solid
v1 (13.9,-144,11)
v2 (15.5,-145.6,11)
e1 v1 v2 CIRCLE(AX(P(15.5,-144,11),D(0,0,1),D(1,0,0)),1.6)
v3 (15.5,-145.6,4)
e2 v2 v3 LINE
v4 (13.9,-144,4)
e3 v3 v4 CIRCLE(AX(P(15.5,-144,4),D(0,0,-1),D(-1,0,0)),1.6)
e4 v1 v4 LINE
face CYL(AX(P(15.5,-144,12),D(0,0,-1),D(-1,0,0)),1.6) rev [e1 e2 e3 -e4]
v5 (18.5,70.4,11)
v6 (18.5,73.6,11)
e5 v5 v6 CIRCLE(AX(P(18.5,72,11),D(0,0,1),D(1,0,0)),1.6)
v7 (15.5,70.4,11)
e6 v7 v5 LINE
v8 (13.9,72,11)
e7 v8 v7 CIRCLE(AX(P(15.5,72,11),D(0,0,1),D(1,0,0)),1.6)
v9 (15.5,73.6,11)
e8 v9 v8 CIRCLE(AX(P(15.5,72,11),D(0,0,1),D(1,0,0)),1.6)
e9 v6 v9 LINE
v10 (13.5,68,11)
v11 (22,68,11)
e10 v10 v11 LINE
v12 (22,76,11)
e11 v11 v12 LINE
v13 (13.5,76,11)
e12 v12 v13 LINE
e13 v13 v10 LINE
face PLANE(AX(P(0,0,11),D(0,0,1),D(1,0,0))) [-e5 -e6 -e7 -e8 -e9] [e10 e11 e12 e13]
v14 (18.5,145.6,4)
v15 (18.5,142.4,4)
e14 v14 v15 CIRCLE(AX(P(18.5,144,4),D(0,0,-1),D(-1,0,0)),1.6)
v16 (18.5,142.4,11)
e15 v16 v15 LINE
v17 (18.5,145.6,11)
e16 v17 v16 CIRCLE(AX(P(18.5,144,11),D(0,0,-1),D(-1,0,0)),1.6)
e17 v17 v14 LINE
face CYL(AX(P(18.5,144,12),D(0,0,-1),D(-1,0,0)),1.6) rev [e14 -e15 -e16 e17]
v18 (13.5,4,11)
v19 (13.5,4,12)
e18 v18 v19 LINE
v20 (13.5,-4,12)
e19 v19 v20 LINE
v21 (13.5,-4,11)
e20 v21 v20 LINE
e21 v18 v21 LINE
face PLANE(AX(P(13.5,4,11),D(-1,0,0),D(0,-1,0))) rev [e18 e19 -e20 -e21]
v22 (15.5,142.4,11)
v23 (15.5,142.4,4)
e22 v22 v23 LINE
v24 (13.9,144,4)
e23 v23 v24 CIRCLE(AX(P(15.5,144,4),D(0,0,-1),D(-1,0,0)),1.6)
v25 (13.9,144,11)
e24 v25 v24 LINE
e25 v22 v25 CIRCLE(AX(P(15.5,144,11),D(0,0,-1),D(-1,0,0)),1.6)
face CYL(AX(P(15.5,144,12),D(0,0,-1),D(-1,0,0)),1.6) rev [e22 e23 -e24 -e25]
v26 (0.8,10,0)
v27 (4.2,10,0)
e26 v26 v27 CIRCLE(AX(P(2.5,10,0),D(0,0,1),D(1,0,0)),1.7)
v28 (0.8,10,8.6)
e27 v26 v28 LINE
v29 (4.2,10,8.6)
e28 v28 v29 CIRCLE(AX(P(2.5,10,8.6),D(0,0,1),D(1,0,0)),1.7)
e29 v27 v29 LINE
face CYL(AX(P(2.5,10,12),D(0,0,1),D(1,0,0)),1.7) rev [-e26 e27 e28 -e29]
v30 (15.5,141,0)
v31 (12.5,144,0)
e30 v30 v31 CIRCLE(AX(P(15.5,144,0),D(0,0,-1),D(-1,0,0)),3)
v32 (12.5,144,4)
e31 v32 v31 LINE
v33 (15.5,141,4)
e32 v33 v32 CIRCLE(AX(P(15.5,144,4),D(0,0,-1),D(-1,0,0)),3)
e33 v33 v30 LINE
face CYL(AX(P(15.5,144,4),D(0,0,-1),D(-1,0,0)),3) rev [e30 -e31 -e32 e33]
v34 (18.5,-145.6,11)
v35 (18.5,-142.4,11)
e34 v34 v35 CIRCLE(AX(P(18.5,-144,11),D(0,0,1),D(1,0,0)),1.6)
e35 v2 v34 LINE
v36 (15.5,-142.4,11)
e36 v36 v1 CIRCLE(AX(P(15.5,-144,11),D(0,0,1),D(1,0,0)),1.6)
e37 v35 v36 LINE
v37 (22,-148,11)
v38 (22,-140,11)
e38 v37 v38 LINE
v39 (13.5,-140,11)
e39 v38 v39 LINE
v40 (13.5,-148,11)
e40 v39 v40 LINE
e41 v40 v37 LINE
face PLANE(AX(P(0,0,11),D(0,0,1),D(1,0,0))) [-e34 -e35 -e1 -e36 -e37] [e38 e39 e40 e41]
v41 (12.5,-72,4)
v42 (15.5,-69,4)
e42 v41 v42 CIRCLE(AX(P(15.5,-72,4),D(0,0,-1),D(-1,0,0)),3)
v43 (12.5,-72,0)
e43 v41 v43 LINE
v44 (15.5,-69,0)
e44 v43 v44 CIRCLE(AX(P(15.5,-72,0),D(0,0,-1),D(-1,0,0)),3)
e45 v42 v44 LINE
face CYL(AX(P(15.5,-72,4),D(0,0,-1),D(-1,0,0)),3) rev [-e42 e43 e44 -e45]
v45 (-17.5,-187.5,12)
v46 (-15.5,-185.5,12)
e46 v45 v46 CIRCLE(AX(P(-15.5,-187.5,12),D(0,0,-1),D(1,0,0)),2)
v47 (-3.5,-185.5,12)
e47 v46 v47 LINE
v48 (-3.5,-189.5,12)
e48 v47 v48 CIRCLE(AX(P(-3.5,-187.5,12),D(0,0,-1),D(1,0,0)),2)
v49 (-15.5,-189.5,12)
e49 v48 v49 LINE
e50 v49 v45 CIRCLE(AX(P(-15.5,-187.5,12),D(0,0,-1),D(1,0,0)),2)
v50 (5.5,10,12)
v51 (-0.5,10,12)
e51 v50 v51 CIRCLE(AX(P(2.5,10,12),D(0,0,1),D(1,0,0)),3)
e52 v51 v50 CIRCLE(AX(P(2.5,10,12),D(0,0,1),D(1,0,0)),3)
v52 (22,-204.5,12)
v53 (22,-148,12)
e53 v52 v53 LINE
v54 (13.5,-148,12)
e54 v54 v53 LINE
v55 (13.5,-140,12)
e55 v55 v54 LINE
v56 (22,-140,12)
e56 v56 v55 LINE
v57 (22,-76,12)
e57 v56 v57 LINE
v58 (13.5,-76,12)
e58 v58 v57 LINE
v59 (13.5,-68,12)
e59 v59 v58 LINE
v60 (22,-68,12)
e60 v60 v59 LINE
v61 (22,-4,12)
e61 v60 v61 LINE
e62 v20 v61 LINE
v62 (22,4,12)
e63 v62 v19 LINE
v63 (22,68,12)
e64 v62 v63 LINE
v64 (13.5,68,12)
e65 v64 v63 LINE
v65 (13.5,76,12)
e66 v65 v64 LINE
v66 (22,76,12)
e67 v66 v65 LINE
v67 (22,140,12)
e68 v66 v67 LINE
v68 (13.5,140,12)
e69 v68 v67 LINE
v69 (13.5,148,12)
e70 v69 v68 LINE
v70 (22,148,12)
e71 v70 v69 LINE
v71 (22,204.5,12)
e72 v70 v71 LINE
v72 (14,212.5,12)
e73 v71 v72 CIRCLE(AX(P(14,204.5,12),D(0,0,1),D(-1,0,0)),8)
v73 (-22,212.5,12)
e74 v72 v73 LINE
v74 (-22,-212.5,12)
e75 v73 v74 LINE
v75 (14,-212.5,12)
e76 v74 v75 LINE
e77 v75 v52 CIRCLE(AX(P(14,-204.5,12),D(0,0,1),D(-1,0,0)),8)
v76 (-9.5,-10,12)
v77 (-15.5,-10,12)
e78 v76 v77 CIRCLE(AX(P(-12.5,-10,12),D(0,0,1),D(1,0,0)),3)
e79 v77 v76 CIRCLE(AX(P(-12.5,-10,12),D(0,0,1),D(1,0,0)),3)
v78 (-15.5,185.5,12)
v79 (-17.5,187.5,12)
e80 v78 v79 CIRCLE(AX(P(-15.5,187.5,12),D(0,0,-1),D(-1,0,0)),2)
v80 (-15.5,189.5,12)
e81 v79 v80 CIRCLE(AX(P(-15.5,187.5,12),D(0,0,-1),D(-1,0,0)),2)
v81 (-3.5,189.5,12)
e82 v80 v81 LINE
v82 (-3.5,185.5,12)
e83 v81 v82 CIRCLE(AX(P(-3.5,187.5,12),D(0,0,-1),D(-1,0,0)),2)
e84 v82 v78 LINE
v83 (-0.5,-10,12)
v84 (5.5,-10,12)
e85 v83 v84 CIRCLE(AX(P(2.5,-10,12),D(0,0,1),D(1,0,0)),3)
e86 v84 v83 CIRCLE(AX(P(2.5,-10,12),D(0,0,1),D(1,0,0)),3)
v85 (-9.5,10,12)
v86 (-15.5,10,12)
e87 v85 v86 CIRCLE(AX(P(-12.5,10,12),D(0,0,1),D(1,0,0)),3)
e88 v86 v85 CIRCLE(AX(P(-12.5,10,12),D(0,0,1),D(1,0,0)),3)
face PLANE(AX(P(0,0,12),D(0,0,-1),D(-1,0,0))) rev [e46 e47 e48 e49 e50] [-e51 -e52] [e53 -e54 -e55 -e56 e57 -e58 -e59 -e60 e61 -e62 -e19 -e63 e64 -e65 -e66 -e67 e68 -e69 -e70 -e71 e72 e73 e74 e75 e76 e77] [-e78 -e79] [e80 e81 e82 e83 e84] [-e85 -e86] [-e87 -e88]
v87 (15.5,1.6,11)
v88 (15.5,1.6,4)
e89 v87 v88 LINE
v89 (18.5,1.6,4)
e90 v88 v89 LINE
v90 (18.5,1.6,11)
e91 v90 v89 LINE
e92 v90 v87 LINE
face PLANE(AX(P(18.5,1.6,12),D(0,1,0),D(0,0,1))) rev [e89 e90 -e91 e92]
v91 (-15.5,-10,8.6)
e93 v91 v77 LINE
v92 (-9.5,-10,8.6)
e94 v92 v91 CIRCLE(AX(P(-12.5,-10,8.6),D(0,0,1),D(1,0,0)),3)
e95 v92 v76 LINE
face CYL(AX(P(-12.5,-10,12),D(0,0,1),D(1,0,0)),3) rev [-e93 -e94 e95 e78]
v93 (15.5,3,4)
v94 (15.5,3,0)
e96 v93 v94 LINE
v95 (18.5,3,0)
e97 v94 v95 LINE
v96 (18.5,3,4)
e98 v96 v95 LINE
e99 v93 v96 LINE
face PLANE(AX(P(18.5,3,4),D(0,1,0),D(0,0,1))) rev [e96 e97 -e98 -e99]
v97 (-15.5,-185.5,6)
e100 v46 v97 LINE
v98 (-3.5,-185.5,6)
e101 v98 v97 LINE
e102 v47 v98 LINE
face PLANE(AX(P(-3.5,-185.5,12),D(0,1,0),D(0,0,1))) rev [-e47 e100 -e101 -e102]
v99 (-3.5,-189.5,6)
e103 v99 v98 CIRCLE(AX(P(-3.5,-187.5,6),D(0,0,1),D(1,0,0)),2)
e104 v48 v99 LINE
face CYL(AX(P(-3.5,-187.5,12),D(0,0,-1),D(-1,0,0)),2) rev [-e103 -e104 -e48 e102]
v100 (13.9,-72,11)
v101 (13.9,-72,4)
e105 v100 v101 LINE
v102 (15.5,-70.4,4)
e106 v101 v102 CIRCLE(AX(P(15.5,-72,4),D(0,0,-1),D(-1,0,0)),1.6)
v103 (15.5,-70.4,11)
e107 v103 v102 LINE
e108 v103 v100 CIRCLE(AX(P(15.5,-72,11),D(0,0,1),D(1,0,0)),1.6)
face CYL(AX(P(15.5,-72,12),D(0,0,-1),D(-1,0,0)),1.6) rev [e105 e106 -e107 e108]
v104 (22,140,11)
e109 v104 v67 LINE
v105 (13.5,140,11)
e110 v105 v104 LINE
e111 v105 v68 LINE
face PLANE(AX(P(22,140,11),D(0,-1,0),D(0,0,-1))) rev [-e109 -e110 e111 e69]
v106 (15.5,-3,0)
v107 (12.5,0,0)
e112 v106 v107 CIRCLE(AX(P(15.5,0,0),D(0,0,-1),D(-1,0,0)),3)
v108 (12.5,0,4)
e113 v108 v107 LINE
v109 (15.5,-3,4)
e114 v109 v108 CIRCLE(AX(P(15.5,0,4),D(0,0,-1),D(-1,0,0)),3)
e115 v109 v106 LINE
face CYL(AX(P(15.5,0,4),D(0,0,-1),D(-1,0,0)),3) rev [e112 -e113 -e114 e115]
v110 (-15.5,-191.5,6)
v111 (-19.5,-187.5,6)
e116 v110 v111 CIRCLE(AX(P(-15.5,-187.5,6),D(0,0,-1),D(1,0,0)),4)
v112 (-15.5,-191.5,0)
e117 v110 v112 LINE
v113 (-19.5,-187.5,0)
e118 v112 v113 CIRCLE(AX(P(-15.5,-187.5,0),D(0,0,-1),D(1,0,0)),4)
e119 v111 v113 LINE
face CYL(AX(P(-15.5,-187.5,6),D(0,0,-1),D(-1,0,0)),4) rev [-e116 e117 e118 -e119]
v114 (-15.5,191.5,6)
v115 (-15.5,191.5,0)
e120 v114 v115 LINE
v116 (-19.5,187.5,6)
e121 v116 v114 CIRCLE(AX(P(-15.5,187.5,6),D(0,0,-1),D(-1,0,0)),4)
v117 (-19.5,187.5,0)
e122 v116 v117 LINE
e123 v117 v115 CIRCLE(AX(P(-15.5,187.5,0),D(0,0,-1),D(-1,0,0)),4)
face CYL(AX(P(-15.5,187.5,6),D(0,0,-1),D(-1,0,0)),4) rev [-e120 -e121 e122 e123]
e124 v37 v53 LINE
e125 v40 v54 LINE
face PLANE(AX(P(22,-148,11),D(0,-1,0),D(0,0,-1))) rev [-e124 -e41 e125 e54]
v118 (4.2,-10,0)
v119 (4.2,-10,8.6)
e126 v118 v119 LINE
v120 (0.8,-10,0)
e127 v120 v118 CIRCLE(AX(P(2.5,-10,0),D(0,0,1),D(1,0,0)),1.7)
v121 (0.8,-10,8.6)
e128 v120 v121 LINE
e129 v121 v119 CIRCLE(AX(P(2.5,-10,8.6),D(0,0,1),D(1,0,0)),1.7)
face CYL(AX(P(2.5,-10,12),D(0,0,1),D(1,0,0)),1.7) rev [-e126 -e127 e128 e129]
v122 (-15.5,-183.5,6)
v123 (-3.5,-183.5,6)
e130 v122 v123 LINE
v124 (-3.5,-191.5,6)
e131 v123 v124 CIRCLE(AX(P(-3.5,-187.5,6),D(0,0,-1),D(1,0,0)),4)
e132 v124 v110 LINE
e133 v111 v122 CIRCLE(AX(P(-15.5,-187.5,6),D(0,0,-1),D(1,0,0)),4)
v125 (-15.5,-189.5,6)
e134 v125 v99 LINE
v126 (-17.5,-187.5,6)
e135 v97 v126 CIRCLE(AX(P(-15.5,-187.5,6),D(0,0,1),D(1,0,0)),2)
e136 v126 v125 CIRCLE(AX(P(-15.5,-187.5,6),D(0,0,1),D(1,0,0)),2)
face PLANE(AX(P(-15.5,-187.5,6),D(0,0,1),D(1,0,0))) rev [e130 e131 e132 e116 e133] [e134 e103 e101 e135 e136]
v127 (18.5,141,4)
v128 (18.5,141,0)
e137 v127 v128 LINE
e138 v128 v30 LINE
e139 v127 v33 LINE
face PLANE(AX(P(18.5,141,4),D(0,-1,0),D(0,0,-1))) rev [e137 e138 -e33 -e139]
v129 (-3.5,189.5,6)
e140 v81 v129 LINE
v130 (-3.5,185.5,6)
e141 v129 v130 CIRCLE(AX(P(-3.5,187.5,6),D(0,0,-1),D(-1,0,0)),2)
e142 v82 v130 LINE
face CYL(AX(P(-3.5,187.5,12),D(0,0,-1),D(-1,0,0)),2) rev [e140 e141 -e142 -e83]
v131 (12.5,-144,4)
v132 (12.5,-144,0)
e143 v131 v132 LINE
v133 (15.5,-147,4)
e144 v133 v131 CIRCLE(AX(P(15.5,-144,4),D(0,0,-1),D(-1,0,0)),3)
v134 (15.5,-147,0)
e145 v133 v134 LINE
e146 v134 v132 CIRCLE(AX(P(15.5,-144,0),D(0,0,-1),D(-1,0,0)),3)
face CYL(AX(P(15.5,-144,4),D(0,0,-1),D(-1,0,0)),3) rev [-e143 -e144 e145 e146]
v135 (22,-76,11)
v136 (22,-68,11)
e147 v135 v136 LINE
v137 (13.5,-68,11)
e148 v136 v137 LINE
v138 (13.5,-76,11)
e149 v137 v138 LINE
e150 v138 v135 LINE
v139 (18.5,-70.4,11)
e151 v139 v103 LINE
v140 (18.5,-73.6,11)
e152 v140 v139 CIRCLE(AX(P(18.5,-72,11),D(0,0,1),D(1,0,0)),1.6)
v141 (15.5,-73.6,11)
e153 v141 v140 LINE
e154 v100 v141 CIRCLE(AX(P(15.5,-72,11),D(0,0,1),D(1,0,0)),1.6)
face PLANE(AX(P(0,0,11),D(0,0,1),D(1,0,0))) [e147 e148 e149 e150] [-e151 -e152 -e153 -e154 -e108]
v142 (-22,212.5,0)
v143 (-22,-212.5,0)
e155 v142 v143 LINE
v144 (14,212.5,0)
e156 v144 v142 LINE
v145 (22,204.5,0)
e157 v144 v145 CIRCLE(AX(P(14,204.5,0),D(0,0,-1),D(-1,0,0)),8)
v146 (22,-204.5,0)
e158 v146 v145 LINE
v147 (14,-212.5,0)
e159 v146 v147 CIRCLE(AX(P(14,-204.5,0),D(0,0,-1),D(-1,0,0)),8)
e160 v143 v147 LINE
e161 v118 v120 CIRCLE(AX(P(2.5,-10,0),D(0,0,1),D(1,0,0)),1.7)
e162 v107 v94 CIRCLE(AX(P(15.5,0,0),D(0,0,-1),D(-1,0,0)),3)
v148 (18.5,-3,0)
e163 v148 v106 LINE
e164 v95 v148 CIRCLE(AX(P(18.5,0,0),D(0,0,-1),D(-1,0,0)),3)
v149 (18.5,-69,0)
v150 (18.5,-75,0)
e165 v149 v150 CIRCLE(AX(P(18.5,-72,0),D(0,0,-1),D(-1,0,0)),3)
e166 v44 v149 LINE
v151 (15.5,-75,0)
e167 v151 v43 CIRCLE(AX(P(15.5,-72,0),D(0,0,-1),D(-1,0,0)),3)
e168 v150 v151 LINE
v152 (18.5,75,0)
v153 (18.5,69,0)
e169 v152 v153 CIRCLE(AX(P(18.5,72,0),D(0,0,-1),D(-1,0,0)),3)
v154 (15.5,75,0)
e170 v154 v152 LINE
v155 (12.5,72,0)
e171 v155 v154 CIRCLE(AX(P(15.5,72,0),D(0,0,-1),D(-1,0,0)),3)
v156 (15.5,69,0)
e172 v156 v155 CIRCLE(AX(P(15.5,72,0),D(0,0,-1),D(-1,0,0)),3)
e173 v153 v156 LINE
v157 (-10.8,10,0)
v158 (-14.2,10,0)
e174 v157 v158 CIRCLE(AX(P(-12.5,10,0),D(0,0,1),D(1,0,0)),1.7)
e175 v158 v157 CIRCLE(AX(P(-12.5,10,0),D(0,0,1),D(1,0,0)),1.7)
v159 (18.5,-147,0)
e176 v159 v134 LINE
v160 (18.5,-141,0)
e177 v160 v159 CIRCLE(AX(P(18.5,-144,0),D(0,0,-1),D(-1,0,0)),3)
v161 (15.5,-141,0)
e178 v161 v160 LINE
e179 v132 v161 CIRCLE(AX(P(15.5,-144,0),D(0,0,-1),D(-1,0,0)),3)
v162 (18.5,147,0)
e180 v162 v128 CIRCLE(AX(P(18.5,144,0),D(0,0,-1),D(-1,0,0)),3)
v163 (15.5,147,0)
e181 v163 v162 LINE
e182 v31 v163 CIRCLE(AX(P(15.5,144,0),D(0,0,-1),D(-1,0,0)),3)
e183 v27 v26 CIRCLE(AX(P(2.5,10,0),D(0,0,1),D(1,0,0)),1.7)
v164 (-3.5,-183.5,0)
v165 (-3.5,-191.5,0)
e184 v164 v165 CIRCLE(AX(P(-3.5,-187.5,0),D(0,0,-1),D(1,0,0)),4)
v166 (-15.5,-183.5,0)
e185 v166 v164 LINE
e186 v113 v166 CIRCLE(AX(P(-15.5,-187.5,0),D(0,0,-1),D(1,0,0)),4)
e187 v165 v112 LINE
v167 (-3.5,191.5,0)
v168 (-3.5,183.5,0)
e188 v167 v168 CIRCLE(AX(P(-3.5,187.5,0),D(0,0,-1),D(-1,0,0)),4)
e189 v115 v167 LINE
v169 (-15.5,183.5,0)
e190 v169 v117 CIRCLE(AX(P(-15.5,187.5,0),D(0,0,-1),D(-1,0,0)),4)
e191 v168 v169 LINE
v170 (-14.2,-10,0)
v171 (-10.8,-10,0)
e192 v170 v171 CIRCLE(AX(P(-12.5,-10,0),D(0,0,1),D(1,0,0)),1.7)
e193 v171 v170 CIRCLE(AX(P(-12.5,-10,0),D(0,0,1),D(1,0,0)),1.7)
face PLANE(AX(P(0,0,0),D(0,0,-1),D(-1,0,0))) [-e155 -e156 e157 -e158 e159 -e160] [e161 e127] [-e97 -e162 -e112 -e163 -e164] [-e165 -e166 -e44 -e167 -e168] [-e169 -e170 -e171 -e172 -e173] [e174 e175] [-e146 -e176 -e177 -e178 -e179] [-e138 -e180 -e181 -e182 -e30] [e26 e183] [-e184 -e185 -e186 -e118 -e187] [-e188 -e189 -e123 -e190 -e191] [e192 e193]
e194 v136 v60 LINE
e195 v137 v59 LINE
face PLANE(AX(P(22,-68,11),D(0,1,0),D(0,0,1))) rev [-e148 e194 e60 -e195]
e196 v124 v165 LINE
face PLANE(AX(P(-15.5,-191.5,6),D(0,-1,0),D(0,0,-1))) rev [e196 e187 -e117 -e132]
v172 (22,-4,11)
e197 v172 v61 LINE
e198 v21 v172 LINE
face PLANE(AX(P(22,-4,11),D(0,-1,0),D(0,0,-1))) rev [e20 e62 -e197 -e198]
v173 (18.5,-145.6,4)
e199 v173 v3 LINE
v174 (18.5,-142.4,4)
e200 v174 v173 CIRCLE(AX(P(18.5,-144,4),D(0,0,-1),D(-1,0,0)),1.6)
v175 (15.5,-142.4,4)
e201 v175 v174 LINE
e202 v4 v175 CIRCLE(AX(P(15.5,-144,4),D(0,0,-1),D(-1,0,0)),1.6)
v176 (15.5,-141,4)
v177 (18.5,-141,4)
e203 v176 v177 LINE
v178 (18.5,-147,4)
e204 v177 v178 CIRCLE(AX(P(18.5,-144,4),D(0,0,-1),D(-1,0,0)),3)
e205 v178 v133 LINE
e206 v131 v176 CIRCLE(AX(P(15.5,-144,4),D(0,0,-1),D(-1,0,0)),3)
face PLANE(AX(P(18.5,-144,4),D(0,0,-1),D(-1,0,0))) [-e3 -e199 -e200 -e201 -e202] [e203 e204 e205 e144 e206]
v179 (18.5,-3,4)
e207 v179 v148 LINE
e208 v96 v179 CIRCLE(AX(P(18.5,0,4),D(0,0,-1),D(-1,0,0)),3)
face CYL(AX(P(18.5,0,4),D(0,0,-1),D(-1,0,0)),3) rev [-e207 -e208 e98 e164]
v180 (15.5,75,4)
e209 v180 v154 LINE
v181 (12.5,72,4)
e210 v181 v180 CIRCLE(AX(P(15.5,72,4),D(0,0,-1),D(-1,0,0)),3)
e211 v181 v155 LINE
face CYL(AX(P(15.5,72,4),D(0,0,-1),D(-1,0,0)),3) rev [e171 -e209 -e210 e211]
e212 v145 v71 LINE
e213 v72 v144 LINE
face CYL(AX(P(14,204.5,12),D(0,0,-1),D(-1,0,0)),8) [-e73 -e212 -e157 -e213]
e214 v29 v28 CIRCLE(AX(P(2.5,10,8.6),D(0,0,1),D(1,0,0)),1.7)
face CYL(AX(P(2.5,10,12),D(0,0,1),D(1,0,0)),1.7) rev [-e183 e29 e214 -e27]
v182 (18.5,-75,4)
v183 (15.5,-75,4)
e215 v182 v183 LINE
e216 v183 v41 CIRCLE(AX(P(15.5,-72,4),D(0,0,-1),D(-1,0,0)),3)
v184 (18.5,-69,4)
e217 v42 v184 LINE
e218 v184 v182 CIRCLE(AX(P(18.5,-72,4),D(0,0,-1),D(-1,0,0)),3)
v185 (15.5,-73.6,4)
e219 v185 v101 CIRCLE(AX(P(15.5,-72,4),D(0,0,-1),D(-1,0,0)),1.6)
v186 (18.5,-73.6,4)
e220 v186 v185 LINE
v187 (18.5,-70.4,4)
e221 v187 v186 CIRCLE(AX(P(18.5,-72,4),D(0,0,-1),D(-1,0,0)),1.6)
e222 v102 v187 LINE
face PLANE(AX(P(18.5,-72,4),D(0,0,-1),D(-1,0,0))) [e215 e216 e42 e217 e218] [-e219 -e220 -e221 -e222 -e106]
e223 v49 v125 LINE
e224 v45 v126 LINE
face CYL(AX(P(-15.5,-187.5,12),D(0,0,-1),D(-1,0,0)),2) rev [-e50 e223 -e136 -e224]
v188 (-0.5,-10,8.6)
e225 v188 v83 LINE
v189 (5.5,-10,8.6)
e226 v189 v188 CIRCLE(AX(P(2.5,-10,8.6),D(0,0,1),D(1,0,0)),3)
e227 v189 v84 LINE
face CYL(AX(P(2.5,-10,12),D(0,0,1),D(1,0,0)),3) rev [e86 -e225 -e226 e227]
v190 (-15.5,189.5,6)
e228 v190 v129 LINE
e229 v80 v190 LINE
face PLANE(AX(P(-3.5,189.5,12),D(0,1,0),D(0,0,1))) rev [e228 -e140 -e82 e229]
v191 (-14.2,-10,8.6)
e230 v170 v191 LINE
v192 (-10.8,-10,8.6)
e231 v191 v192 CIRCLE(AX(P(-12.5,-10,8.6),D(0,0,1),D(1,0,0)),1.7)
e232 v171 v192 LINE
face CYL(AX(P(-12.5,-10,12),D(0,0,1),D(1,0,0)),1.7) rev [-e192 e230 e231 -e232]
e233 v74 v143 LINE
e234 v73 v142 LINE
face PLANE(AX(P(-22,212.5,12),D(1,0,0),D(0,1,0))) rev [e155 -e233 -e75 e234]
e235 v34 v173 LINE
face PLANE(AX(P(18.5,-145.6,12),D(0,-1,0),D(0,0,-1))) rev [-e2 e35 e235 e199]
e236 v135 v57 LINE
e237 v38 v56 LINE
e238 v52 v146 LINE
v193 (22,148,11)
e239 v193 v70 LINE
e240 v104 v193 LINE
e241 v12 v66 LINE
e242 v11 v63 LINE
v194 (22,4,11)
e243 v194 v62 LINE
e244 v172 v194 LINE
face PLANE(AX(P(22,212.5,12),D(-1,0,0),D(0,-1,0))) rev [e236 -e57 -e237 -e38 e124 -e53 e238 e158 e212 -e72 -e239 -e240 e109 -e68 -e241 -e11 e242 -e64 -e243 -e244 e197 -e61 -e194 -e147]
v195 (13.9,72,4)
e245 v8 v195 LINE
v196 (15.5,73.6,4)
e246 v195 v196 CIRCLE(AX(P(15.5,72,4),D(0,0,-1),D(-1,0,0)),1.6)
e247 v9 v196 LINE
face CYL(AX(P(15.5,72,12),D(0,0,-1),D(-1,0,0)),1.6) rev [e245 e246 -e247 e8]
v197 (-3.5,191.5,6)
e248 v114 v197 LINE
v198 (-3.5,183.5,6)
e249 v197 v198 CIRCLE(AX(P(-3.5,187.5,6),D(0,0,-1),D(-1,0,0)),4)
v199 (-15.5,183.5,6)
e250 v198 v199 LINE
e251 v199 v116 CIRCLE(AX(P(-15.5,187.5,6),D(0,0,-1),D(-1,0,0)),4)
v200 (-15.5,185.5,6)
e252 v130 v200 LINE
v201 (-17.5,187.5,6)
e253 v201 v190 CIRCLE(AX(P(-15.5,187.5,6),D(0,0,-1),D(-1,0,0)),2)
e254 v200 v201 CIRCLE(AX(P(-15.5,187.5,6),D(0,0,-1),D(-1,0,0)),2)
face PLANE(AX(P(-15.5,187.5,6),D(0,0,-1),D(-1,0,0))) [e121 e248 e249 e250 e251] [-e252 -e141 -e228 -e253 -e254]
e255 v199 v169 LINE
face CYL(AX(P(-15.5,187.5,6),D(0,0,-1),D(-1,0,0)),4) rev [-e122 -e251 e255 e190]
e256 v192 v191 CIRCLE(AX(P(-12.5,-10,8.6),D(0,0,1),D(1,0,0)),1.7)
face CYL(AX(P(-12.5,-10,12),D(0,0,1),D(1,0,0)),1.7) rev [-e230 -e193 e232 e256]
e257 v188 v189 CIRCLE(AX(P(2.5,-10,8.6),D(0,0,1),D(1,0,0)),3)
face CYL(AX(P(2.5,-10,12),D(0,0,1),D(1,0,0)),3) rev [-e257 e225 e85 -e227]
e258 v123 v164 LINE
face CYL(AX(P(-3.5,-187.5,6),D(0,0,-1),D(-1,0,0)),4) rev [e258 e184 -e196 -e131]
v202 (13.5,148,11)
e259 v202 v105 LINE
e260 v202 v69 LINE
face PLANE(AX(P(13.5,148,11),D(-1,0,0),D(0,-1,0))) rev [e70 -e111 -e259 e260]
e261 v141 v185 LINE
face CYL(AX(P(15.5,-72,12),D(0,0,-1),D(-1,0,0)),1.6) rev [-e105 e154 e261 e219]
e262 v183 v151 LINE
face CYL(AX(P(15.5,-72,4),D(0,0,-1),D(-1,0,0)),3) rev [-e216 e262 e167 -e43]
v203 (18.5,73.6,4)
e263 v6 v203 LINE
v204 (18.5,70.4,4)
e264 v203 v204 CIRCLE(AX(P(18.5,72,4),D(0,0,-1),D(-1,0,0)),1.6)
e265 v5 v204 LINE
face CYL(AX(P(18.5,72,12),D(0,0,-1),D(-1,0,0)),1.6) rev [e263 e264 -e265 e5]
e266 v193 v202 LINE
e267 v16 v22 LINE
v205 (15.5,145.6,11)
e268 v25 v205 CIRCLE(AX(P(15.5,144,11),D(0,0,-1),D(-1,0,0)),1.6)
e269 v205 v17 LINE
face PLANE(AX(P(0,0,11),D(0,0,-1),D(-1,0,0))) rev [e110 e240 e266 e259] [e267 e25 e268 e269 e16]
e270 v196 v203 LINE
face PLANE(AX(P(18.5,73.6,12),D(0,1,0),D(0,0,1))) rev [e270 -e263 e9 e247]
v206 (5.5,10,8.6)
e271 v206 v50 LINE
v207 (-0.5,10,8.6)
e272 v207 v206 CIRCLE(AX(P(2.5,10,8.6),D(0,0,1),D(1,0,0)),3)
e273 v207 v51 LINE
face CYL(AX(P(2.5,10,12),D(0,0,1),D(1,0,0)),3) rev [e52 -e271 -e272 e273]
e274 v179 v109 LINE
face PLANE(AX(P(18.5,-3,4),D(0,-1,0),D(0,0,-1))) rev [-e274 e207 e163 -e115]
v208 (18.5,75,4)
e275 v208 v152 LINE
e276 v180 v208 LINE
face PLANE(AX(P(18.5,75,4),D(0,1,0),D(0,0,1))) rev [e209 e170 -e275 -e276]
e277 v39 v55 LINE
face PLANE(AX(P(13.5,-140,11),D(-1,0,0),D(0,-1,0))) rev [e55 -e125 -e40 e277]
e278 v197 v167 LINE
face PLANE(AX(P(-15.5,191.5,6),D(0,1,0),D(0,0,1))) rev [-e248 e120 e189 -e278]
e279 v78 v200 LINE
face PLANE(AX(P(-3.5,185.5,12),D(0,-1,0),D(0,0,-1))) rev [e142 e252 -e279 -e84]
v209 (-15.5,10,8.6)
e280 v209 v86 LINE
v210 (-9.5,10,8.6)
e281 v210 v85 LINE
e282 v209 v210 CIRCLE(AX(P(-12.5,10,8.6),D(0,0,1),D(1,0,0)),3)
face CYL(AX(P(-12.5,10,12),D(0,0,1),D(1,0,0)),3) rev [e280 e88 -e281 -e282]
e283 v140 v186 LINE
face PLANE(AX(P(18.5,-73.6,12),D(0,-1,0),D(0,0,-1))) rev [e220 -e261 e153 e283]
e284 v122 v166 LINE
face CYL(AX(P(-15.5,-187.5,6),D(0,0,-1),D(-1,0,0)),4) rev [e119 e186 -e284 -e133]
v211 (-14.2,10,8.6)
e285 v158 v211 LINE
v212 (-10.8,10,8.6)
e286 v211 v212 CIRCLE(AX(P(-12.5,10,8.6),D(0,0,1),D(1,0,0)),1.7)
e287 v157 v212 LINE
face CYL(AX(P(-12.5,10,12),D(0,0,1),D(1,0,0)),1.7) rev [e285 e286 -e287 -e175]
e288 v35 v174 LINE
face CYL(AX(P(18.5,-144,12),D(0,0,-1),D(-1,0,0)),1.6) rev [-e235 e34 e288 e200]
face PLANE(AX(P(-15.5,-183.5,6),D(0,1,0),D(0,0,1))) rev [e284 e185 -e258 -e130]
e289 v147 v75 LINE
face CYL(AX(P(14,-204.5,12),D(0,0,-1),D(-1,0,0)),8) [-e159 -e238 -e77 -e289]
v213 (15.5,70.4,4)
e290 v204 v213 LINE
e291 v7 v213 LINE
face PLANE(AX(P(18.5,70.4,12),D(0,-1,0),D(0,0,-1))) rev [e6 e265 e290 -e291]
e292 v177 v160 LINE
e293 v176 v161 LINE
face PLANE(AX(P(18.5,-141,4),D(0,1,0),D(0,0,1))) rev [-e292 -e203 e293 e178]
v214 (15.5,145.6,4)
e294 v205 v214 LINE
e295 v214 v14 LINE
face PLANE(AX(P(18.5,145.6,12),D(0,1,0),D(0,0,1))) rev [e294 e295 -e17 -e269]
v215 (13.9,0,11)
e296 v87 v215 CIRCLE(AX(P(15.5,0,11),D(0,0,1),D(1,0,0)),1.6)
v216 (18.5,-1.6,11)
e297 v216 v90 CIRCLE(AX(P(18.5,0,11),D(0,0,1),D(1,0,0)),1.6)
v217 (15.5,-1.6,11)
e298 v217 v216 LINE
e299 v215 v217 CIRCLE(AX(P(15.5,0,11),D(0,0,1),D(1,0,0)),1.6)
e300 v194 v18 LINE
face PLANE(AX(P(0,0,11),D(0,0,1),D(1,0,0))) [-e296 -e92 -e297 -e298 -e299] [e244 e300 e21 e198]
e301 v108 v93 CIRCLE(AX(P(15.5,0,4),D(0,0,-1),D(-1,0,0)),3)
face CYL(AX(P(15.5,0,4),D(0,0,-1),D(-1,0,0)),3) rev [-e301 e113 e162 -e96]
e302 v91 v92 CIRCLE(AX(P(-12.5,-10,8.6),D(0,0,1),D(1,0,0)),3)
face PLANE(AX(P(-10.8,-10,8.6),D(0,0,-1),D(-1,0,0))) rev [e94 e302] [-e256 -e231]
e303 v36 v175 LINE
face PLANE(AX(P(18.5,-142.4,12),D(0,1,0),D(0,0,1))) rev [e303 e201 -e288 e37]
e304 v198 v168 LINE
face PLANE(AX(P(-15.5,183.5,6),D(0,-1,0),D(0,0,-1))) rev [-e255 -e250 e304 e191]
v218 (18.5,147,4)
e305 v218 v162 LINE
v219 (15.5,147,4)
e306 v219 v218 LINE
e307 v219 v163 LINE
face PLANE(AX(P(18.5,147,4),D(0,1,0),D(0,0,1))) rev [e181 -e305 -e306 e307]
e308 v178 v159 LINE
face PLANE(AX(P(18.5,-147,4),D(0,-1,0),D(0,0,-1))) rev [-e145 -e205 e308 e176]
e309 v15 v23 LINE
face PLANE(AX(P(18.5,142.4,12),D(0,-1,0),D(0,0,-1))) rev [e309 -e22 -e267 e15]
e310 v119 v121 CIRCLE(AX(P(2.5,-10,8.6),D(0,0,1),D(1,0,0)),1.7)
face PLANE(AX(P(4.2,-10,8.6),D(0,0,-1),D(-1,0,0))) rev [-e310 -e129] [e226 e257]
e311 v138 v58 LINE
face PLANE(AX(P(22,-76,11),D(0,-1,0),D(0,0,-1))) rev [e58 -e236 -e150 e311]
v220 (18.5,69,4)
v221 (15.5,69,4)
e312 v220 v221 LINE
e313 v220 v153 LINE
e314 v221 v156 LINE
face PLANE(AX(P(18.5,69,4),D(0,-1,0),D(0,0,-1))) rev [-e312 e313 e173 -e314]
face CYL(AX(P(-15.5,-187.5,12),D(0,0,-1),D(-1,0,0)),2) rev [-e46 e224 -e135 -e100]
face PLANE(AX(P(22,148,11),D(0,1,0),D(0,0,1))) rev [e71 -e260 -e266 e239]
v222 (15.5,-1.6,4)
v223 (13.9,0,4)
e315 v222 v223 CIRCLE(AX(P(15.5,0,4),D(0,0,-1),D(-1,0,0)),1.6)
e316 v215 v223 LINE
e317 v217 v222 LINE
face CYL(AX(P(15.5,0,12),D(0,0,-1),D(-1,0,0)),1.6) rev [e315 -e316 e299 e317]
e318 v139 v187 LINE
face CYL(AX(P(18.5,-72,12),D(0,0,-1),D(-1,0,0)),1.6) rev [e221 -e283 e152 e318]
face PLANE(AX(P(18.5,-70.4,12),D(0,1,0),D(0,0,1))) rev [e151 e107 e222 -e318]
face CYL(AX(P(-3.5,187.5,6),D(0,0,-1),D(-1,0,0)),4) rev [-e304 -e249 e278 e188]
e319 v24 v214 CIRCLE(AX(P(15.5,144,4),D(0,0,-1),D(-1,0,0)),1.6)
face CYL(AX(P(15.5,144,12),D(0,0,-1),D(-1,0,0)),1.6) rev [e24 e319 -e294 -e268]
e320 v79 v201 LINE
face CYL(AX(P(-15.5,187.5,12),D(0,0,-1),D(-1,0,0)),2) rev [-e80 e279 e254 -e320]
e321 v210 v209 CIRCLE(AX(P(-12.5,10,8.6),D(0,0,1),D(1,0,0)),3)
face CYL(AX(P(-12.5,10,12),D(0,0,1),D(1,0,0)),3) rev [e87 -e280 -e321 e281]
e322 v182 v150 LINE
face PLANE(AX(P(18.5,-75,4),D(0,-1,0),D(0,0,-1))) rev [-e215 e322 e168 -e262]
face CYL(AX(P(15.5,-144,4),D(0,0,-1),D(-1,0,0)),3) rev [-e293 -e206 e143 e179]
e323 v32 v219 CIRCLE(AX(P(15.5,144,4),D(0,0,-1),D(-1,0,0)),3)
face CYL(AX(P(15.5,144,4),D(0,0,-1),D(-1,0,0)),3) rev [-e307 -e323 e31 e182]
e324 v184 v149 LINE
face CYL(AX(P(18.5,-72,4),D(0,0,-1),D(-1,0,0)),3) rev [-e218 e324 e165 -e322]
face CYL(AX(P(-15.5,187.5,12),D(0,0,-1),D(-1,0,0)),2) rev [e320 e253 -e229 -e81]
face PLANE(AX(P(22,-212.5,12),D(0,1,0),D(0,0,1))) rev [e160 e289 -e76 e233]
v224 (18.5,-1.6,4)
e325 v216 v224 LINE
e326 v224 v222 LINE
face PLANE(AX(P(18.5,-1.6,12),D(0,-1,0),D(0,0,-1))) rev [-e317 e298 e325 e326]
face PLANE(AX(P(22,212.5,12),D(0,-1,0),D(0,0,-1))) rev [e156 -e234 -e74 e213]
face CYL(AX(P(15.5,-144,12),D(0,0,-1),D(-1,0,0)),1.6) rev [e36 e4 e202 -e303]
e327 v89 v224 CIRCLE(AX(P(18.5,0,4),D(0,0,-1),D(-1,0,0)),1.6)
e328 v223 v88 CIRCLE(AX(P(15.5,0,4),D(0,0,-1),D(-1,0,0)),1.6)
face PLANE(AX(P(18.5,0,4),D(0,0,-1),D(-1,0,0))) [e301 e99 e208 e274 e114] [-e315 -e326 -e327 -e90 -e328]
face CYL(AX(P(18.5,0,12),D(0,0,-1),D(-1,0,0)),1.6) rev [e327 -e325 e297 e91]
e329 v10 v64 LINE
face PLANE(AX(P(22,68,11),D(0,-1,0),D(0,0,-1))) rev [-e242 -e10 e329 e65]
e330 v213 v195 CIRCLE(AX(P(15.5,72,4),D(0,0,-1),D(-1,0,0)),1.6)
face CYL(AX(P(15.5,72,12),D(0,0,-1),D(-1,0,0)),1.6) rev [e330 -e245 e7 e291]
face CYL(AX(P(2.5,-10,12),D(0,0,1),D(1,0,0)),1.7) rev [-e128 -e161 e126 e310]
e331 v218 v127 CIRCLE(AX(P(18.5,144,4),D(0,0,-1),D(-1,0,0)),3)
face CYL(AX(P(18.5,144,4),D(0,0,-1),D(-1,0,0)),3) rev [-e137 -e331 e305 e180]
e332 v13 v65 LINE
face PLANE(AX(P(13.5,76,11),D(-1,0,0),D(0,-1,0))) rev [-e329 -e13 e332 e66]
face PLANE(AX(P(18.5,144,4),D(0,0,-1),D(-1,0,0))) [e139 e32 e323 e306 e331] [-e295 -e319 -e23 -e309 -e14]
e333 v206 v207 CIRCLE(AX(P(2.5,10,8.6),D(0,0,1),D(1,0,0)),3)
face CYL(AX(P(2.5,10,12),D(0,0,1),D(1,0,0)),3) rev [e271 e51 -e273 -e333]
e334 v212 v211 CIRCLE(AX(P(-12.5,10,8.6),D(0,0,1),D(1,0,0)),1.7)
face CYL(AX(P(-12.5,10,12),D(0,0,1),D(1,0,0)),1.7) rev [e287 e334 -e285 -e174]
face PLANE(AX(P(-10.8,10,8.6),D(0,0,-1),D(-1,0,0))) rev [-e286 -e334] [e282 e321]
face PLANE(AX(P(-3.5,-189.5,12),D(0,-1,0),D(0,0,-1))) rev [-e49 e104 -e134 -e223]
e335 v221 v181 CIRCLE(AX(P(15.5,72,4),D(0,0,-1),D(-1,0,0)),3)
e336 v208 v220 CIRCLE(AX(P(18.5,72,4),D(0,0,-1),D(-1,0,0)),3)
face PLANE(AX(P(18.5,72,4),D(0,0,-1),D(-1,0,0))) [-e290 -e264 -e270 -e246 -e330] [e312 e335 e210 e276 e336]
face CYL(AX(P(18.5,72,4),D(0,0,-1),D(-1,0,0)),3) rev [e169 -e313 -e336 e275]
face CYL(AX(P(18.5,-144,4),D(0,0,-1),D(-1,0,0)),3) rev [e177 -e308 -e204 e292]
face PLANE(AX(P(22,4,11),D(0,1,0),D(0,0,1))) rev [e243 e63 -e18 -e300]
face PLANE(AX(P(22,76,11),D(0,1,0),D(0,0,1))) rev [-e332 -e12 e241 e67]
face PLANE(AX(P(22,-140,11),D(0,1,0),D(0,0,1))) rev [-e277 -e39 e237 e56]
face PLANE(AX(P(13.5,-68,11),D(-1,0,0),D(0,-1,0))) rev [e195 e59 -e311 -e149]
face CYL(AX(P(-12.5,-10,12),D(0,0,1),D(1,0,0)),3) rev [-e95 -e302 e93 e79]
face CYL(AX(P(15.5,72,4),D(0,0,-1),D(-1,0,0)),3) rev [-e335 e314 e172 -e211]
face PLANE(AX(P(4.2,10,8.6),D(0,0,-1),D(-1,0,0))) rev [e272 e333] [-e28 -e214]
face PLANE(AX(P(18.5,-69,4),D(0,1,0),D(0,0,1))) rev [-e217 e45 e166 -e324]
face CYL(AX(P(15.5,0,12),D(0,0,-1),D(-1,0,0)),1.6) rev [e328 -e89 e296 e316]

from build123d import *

# Parameters (mm, degrees)
SKETCH_1_W                = 44
SKETCH_1_H                = 425
EXTRUDE_1_DEPTH           = 12
FILLET_1_R                = 8
CUT_EXTRUDE_1_DEPTH       = 6
CUT_EXTRUDE_2_DEPTH       = 214.972544968
SKETCH_5_W                = 8.5
SKETCH_5_H                = 8
CUT_EXTRUDE_3_DEPTH       = 1
CUT_EXTRUDE_4_DEPTH       = 4
CUT_EXTRUDE_5_DEPTH       = 214.785523364
PATTERN_LINEAR_1_COUNT    = 5
PATTERN_LINEAR_1_PITCH    = 72
HOLE_WIZARD_1_D           = 3.4
HOLE_WIZARD_1_CBORE_D     = 6
HOLE_WIZARD_1_CBORE_DEPTH = 3.4


with BuildPart() as part:
    # 草图1 → 凸台-拉伸1 (new body)
    with BuildSketch(Plane.XY):
        Rectangle(SKETCH_1_W, SKETCH_1_H)
    extrude(amount=EXTRUDE_1_DEPTH)

    # 圆角1
    fillet_1_edges = [part.edges().sort_by_distance(p)[0] for p in [
        (22, 212.5, 6),
        (22, -212.5, 6),
    ]]
    fillet(fillet_1_edges, radius=FILLET_1_R)

    # 草图3 → 切除-拉伸1 (cut)
    with BuildSketch(Plane(origin=(0, 0, 0), x_dir=(-1, 0, 0), z_dir=(0, 0, -1))):
        with BuildLine():
            Line((15.5, 183.5), (3.5, 183.5))
            ThreePointArc((3.5, 183.5), (-0.5, 187.5), (3.5, 191.5))
            Line((3.5, 191.5), (15.5, 191.5))
            ThreePointArc((15.5, 191.5), (19.5, 187.5), (15.5, 183.5))
        make_face()
        with BuildLine():
            Line((15.5, -183.5), (3.5, -183.5))
            ThreePointArc((3.5, -183.5), (-0.5, -187.5), (3.5, -191.5))
            Line((3.5, -191.5), (15.5, -191.5))
            ThreePointArc((15.5, -191.5), (19.5, -187.5), (15.5, -183.5))
        make_face()
    extrude(amount=-CUT_EXTRUDE_1_DEPTH, mode=Mode.SUBTRACT)

    # 草图4 → 切除-拉伸2 (cut, through all)
    with BuildSketch(Plane(origin=(0, 0, 0), x_dir=(-1, 0, 0), z_dir=(0, 0, -1))):
        with BuildLine():
            Line((3.5, 189.5), (15.5, 189.5))
            ThreePointArc((15.5, 189.5), (17.5, 187.5), (15.5, 185.5))
            Line((15.5, 185.5), (3.5, 185.5))
            ThreePointArc((3.5, 185.5), (1.5, 187.5), (3.5, 189.5))
        make_face()
        with BuildLine():
            Line((3.5, -189.5), (15.5, -189.5))
            ThreePointArc((15.5, -189.5), (17.5, -187.5), (15.5, -185.5))
            Line((15.5, -185.5), (3.5, -185.5))
            ThreePointArc((3.5, -185.5), (1.5, -187.5), (3.5, -189.5))
        make_face()
    extrude(amount=-CUT_EXTRUDE_2_DEPTH, mode=Mode.SUBTRACT)

    # 草图5 → 切除-拉伸3 (cut)
    with BuildSketch(Plane.XY.offset(12)):
        with Locations((17.75, 144)):
            Rectangle(SKETCH_5_W, SKETCH_5_H)
        with Locations((17.75, 72)):
            Rectangle(SKETCH_5_W, SKETCH_5_H)
        with Locations((17.75, 0)):
            Rectangle(SKETCH_5_W, SKETCH_5_H)
        with Locations((17.75, -72)):
            Rectangle(SKETCH_5_W, SKETCH_5_H)
        with Locations((17.75, -144)):
            Rectangle(SKETCH_5_W, SKETCH_5_H)
    extrude(amount=-CUT_EXTRUDE_3_DEPTH, mode=Mode.SUBTRACT)

    # 草图6 → 切除-拉伸4 (cut)
    with BuildSketch(Plane(origin=(0, 0, 0), x_dir=(-1, 0, 0), z_dir=(0, 0, -1))):
        with BuildLine():
            Line((-18.5, 147), (-15.5, 147))
            ThreePointArc((-15.5, 147), (-12.5, 144), (-15.5, 141))
            Line((-15.5, 141), (-18.5, 141))
            ThreePointArc((-18.5, 141), (-21.5, 144), (-18.5, 147))
        make_face()
    cut_extrude_4 = extrude(amount=-CUT_EXTRUDE_4_DEPTH, mode=Mode.SUBTRACT)

    # 草图7 → 切除-拉伸5 (cut, through all)
    with BuildSketch(Plane(origin=(0, 0, 4), x_dir=(-1, 0, 0), z_dir=(0, 0, -1))):
        with BuildLine():
            Line((-18.5, 145.6), (-15.5, 145.6))
            ThreePointArc((-15.5, 145.6), (-13.9, 144), (-15.5, 142.4))
            Line((-15.5, 142.4), (-18.5, 142.4))
            ThreePointArc((-18.5, 142.4), (-20.1, 144), (-18.5, 145.6))
        make_face()
    cut_extrude_5 = extrude(amount=-CUT_EXTRUDE_5_DEPTH, mode=Mode.SUBTRACT)

    # 阵列(线性)1: 切除-拉伸4, 切除-拉伸5 ×5
    with Locations(*[(0, -i * PATTERN_LINEAR_1_PITCH, 0) for i in range(1, PATTERN_LINEAR_1_COUNT)]):
        add(cut_extrude_4, mode=Mode.SUBTRACT)
        add(cut_extrude_5, mode=Mode.SUBTRACT)

    # 打孔尺寸根据内六角圆柱头螺钉的类型1 (through all)
    with Locations(Plane.XY.offset(12)):
        with Locations((2.5, 10), (-12.5, 10), (2.5, -10), (-12.5, -10)):
            CounterBoreHole(HOLE_WIZARD_1_D / 2, HOLE_WIZARD_1_CBORE_D / 2, HOLE_WIZARD_1_CBORE_DEPTH)


solid = part.part
